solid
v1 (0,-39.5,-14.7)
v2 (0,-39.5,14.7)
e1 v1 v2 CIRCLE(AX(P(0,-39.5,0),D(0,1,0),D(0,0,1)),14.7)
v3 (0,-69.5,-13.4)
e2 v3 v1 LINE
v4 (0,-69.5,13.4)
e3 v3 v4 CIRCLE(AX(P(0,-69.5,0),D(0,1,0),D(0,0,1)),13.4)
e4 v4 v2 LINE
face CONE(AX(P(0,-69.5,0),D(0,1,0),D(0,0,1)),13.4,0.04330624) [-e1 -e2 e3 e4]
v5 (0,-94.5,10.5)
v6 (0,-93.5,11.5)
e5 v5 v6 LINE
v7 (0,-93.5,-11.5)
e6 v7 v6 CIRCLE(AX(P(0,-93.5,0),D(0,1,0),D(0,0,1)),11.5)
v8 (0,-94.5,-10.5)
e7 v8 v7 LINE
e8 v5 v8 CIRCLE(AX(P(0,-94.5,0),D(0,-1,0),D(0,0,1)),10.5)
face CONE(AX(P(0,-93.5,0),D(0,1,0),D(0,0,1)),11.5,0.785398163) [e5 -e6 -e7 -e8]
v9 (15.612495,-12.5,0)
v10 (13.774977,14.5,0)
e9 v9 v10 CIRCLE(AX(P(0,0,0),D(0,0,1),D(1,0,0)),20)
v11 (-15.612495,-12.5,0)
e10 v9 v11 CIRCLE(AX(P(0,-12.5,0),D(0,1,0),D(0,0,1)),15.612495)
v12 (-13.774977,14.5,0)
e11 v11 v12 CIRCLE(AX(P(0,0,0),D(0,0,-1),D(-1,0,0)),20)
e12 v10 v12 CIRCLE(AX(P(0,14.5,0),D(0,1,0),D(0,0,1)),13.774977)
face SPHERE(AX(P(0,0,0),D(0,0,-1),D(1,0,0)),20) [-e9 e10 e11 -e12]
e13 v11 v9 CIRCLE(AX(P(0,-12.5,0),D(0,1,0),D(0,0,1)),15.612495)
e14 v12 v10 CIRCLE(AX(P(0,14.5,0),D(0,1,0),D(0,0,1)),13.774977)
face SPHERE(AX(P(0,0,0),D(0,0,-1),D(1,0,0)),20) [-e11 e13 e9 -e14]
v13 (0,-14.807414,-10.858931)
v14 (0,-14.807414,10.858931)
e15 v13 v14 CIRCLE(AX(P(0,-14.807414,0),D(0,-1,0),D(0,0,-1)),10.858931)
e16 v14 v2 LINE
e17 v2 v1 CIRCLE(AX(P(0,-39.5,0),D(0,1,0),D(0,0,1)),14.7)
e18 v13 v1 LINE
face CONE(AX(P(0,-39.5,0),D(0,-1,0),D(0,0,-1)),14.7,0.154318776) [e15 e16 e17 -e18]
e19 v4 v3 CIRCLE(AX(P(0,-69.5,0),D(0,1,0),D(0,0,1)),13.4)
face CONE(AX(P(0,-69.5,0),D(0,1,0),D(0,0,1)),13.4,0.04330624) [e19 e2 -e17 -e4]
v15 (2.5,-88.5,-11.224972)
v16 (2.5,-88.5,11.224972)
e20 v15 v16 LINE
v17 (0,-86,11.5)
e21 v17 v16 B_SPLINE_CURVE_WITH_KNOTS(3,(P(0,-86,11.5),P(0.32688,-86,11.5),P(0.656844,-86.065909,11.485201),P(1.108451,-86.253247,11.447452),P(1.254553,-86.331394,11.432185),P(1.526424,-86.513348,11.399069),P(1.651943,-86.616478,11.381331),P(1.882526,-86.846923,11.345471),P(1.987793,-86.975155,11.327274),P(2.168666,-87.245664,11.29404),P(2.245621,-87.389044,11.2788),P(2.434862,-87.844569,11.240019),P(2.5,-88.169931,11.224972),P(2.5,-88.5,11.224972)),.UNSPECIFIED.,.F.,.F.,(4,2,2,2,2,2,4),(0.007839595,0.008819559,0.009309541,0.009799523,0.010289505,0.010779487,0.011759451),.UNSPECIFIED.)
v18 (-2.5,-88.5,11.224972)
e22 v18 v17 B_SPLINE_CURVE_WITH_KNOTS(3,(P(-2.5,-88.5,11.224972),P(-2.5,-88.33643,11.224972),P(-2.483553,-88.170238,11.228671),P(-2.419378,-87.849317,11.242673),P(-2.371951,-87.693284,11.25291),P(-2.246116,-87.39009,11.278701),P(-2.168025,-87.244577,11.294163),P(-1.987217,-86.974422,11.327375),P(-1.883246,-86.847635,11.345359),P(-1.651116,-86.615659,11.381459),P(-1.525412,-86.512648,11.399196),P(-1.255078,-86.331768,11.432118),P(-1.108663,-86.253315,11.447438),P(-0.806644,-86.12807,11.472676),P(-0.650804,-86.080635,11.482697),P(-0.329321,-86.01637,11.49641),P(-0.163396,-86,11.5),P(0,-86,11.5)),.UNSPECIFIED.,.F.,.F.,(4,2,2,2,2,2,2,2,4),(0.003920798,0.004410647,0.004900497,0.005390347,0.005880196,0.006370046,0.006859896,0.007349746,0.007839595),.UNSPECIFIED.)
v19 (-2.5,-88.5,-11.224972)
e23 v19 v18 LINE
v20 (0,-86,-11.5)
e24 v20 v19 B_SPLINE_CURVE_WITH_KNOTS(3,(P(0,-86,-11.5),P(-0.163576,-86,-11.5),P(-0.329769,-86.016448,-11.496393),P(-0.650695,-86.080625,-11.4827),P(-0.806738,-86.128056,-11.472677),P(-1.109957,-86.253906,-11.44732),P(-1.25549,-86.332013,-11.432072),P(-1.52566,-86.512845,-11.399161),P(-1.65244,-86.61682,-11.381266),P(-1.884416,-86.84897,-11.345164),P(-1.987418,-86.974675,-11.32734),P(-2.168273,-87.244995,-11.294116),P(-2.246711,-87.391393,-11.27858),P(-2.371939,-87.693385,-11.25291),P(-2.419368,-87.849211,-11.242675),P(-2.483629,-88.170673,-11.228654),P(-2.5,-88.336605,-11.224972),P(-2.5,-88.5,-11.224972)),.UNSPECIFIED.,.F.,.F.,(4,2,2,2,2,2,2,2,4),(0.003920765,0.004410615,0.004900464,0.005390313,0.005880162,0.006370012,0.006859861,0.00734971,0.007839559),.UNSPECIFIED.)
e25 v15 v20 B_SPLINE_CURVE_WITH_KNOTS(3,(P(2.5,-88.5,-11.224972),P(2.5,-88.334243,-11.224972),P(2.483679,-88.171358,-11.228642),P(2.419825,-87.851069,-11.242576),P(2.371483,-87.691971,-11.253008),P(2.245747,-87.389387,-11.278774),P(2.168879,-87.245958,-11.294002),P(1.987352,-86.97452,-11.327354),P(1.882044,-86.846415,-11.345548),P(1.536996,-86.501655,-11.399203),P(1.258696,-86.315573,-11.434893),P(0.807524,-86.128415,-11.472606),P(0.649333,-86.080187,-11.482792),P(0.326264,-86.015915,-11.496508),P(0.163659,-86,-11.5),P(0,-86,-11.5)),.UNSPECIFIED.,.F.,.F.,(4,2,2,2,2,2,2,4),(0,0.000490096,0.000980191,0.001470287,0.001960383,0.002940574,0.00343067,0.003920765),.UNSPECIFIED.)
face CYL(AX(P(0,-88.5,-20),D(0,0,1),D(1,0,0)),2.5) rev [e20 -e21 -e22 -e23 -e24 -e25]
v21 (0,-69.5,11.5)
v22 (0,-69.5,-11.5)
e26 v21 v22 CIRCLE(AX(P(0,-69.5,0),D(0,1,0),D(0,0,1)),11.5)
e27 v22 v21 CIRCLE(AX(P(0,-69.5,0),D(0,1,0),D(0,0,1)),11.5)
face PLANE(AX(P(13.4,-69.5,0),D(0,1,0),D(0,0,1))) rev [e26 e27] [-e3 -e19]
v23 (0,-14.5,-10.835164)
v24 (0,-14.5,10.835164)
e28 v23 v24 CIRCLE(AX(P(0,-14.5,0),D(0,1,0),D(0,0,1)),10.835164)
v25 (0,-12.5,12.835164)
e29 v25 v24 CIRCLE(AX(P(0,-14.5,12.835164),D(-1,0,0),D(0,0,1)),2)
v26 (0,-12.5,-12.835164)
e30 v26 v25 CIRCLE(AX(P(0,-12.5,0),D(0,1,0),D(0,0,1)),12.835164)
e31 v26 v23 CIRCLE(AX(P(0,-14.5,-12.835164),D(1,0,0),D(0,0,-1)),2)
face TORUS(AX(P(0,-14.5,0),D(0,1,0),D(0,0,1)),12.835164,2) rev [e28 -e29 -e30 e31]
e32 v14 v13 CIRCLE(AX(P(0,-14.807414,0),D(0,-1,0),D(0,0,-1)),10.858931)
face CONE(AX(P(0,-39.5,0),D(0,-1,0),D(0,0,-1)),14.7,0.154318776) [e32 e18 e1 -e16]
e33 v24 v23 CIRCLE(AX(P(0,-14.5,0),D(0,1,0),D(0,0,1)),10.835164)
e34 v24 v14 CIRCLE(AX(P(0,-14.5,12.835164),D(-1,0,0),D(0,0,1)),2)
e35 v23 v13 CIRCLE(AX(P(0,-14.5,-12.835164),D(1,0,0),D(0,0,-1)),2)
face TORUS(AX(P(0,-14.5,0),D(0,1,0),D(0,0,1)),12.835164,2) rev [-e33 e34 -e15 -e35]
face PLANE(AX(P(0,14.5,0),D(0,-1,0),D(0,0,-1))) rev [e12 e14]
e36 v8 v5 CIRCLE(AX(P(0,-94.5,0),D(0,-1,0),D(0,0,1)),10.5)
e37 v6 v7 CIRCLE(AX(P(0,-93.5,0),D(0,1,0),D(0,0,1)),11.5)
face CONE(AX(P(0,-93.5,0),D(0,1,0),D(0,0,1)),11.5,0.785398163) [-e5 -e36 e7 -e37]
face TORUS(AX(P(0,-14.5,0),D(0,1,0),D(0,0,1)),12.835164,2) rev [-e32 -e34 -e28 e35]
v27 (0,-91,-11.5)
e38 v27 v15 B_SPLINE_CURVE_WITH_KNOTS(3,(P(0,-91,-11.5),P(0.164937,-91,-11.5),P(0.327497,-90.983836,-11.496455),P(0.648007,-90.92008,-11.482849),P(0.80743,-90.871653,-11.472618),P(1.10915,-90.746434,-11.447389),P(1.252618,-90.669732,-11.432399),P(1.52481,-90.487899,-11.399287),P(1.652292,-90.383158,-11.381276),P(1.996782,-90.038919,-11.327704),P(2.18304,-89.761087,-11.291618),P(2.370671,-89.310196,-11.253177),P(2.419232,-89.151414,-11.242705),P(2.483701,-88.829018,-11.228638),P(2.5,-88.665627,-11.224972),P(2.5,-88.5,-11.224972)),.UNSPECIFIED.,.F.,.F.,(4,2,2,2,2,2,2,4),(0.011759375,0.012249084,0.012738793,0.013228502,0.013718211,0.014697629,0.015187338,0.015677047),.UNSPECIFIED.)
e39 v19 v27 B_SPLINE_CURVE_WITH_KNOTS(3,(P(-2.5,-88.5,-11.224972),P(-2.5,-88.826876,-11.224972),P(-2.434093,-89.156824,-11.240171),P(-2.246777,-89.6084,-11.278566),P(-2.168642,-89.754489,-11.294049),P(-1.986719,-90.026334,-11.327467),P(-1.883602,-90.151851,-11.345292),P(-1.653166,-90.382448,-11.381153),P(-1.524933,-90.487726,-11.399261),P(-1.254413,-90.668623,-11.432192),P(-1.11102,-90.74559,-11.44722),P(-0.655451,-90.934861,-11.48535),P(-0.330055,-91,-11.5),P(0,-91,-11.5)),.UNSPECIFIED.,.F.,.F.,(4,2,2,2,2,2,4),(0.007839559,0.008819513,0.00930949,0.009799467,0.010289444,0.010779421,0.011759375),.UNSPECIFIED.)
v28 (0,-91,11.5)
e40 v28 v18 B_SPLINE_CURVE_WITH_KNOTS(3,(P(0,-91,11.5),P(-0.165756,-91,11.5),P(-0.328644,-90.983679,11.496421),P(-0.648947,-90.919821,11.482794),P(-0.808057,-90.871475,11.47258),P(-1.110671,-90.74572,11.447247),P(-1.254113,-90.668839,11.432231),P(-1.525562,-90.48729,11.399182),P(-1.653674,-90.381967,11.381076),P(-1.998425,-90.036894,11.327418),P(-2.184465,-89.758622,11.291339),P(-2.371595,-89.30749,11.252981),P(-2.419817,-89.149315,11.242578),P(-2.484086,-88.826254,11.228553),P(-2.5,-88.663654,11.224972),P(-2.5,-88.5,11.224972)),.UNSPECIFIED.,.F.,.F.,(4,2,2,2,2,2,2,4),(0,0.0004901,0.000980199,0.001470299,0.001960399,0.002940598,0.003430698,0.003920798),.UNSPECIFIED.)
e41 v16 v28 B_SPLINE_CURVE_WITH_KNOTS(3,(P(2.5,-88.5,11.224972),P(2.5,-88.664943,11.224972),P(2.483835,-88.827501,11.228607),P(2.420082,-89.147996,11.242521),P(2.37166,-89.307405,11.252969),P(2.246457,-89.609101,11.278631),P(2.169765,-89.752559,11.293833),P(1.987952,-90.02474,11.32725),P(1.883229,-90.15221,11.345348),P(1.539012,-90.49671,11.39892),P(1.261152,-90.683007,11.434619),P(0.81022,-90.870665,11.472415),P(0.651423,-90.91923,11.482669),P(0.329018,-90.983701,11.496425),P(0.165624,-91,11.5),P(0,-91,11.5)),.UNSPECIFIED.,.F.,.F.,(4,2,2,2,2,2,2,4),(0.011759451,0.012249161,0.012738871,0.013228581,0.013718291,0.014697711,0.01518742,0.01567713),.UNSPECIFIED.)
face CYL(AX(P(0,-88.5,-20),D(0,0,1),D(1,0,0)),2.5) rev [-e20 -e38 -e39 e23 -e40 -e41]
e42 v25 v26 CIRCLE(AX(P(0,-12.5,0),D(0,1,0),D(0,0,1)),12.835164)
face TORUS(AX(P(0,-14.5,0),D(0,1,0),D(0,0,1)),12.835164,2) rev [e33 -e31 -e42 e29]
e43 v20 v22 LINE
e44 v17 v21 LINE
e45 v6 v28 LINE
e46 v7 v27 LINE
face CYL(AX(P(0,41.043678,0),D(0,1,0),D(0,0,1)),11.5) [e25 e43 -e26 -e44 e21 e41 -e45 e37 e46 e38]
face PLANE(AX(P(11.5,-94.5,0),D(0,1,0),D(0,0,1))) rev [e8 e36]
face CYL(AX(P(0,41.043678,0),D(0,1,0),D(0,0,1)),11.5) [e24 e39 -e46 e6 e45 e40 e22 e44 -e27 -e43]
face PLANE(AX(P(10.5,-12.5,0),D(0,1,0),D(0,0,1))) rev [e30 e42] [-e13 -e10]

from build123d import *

# Parameters (mm, degrees)
CHAMFER_1_SIZE           = 1
FILLET_1_R               = 2
CUT_EXTRUDE_1_DEPTH      = 99.642029582
CUT_EXTRUDE_1_DEPTH_BACK = 99.642029582
SKETCH_3_R               = 2.5


with BuildPart() as part:
    # 草图1 → 旋转1 (revolve)
    with BuildSketch(Plane.XY, mode=Mode.PRIVATE) as revolve_1_sk:
        with BuildLine():
            Line((0, 14.5), (13.774977314, 14.5))
            ThreePointArc((13.774977314, 14.5), (19.953843795, 1.357982993), (15.612494996, -12.5))
            Line((15.612494996, -12.5), (10.5, -12.5))
            Line((10.5, -12.5), (14.7, -39.5))
            Line((14.7, -39.5), (13.4, -69.5))
            Line((13.4, -69.5), (11.5, -69.5))
            Line((11.5, -69.5), (11.5, -94.5))
            Line((11.5, -94.5), (0, -94.5))
            Line((0, -94.5), (0, -12.5))
            Line((0, -12.5), (0, 14.5))
        make_face()
    revolve(revolve_1_sk.sketch.rotate(Axis((0, 41.043678396, 0), (0, -1, 0)), 90), axis=Axis((0, 41.043678396, 0), (0, -1, 0)))

    # 倒角1
    chamfer_1_edges = [part.edges().sort_by_distance(p)[0] for p in [
        (0, -94.5, -11.5),
    ]]
    chamfer(chamfer_1_edges, length=CHAMFER_1_SIZE)

    # 圆角1
    fillet_1_edges = [part.edges().sort_by_distance(p)[0] for p in [
        (0, -12.5, -10.5),
    ]]
    fillet(fillet_1_edges, radius=FILLET_1_R)

    # 草图3 → 切除-拉伸1 (cut, two sides: drawn at the far end of the back side and taken through both)
    with BuildSketch(Plane.XY.offset(-CUT_EXTRUDE_1_DEPTH_BACK)):
        with Locations((0, -88.5)):
            Circle(SKETCH_3_R)
    extrude(amount=CUT_EXTRUDE_1_DEPTH + CUT_EXTRUDE_1_DEPTH_BACK, mode=Mode.SUBTRACT)


solid = part.part
